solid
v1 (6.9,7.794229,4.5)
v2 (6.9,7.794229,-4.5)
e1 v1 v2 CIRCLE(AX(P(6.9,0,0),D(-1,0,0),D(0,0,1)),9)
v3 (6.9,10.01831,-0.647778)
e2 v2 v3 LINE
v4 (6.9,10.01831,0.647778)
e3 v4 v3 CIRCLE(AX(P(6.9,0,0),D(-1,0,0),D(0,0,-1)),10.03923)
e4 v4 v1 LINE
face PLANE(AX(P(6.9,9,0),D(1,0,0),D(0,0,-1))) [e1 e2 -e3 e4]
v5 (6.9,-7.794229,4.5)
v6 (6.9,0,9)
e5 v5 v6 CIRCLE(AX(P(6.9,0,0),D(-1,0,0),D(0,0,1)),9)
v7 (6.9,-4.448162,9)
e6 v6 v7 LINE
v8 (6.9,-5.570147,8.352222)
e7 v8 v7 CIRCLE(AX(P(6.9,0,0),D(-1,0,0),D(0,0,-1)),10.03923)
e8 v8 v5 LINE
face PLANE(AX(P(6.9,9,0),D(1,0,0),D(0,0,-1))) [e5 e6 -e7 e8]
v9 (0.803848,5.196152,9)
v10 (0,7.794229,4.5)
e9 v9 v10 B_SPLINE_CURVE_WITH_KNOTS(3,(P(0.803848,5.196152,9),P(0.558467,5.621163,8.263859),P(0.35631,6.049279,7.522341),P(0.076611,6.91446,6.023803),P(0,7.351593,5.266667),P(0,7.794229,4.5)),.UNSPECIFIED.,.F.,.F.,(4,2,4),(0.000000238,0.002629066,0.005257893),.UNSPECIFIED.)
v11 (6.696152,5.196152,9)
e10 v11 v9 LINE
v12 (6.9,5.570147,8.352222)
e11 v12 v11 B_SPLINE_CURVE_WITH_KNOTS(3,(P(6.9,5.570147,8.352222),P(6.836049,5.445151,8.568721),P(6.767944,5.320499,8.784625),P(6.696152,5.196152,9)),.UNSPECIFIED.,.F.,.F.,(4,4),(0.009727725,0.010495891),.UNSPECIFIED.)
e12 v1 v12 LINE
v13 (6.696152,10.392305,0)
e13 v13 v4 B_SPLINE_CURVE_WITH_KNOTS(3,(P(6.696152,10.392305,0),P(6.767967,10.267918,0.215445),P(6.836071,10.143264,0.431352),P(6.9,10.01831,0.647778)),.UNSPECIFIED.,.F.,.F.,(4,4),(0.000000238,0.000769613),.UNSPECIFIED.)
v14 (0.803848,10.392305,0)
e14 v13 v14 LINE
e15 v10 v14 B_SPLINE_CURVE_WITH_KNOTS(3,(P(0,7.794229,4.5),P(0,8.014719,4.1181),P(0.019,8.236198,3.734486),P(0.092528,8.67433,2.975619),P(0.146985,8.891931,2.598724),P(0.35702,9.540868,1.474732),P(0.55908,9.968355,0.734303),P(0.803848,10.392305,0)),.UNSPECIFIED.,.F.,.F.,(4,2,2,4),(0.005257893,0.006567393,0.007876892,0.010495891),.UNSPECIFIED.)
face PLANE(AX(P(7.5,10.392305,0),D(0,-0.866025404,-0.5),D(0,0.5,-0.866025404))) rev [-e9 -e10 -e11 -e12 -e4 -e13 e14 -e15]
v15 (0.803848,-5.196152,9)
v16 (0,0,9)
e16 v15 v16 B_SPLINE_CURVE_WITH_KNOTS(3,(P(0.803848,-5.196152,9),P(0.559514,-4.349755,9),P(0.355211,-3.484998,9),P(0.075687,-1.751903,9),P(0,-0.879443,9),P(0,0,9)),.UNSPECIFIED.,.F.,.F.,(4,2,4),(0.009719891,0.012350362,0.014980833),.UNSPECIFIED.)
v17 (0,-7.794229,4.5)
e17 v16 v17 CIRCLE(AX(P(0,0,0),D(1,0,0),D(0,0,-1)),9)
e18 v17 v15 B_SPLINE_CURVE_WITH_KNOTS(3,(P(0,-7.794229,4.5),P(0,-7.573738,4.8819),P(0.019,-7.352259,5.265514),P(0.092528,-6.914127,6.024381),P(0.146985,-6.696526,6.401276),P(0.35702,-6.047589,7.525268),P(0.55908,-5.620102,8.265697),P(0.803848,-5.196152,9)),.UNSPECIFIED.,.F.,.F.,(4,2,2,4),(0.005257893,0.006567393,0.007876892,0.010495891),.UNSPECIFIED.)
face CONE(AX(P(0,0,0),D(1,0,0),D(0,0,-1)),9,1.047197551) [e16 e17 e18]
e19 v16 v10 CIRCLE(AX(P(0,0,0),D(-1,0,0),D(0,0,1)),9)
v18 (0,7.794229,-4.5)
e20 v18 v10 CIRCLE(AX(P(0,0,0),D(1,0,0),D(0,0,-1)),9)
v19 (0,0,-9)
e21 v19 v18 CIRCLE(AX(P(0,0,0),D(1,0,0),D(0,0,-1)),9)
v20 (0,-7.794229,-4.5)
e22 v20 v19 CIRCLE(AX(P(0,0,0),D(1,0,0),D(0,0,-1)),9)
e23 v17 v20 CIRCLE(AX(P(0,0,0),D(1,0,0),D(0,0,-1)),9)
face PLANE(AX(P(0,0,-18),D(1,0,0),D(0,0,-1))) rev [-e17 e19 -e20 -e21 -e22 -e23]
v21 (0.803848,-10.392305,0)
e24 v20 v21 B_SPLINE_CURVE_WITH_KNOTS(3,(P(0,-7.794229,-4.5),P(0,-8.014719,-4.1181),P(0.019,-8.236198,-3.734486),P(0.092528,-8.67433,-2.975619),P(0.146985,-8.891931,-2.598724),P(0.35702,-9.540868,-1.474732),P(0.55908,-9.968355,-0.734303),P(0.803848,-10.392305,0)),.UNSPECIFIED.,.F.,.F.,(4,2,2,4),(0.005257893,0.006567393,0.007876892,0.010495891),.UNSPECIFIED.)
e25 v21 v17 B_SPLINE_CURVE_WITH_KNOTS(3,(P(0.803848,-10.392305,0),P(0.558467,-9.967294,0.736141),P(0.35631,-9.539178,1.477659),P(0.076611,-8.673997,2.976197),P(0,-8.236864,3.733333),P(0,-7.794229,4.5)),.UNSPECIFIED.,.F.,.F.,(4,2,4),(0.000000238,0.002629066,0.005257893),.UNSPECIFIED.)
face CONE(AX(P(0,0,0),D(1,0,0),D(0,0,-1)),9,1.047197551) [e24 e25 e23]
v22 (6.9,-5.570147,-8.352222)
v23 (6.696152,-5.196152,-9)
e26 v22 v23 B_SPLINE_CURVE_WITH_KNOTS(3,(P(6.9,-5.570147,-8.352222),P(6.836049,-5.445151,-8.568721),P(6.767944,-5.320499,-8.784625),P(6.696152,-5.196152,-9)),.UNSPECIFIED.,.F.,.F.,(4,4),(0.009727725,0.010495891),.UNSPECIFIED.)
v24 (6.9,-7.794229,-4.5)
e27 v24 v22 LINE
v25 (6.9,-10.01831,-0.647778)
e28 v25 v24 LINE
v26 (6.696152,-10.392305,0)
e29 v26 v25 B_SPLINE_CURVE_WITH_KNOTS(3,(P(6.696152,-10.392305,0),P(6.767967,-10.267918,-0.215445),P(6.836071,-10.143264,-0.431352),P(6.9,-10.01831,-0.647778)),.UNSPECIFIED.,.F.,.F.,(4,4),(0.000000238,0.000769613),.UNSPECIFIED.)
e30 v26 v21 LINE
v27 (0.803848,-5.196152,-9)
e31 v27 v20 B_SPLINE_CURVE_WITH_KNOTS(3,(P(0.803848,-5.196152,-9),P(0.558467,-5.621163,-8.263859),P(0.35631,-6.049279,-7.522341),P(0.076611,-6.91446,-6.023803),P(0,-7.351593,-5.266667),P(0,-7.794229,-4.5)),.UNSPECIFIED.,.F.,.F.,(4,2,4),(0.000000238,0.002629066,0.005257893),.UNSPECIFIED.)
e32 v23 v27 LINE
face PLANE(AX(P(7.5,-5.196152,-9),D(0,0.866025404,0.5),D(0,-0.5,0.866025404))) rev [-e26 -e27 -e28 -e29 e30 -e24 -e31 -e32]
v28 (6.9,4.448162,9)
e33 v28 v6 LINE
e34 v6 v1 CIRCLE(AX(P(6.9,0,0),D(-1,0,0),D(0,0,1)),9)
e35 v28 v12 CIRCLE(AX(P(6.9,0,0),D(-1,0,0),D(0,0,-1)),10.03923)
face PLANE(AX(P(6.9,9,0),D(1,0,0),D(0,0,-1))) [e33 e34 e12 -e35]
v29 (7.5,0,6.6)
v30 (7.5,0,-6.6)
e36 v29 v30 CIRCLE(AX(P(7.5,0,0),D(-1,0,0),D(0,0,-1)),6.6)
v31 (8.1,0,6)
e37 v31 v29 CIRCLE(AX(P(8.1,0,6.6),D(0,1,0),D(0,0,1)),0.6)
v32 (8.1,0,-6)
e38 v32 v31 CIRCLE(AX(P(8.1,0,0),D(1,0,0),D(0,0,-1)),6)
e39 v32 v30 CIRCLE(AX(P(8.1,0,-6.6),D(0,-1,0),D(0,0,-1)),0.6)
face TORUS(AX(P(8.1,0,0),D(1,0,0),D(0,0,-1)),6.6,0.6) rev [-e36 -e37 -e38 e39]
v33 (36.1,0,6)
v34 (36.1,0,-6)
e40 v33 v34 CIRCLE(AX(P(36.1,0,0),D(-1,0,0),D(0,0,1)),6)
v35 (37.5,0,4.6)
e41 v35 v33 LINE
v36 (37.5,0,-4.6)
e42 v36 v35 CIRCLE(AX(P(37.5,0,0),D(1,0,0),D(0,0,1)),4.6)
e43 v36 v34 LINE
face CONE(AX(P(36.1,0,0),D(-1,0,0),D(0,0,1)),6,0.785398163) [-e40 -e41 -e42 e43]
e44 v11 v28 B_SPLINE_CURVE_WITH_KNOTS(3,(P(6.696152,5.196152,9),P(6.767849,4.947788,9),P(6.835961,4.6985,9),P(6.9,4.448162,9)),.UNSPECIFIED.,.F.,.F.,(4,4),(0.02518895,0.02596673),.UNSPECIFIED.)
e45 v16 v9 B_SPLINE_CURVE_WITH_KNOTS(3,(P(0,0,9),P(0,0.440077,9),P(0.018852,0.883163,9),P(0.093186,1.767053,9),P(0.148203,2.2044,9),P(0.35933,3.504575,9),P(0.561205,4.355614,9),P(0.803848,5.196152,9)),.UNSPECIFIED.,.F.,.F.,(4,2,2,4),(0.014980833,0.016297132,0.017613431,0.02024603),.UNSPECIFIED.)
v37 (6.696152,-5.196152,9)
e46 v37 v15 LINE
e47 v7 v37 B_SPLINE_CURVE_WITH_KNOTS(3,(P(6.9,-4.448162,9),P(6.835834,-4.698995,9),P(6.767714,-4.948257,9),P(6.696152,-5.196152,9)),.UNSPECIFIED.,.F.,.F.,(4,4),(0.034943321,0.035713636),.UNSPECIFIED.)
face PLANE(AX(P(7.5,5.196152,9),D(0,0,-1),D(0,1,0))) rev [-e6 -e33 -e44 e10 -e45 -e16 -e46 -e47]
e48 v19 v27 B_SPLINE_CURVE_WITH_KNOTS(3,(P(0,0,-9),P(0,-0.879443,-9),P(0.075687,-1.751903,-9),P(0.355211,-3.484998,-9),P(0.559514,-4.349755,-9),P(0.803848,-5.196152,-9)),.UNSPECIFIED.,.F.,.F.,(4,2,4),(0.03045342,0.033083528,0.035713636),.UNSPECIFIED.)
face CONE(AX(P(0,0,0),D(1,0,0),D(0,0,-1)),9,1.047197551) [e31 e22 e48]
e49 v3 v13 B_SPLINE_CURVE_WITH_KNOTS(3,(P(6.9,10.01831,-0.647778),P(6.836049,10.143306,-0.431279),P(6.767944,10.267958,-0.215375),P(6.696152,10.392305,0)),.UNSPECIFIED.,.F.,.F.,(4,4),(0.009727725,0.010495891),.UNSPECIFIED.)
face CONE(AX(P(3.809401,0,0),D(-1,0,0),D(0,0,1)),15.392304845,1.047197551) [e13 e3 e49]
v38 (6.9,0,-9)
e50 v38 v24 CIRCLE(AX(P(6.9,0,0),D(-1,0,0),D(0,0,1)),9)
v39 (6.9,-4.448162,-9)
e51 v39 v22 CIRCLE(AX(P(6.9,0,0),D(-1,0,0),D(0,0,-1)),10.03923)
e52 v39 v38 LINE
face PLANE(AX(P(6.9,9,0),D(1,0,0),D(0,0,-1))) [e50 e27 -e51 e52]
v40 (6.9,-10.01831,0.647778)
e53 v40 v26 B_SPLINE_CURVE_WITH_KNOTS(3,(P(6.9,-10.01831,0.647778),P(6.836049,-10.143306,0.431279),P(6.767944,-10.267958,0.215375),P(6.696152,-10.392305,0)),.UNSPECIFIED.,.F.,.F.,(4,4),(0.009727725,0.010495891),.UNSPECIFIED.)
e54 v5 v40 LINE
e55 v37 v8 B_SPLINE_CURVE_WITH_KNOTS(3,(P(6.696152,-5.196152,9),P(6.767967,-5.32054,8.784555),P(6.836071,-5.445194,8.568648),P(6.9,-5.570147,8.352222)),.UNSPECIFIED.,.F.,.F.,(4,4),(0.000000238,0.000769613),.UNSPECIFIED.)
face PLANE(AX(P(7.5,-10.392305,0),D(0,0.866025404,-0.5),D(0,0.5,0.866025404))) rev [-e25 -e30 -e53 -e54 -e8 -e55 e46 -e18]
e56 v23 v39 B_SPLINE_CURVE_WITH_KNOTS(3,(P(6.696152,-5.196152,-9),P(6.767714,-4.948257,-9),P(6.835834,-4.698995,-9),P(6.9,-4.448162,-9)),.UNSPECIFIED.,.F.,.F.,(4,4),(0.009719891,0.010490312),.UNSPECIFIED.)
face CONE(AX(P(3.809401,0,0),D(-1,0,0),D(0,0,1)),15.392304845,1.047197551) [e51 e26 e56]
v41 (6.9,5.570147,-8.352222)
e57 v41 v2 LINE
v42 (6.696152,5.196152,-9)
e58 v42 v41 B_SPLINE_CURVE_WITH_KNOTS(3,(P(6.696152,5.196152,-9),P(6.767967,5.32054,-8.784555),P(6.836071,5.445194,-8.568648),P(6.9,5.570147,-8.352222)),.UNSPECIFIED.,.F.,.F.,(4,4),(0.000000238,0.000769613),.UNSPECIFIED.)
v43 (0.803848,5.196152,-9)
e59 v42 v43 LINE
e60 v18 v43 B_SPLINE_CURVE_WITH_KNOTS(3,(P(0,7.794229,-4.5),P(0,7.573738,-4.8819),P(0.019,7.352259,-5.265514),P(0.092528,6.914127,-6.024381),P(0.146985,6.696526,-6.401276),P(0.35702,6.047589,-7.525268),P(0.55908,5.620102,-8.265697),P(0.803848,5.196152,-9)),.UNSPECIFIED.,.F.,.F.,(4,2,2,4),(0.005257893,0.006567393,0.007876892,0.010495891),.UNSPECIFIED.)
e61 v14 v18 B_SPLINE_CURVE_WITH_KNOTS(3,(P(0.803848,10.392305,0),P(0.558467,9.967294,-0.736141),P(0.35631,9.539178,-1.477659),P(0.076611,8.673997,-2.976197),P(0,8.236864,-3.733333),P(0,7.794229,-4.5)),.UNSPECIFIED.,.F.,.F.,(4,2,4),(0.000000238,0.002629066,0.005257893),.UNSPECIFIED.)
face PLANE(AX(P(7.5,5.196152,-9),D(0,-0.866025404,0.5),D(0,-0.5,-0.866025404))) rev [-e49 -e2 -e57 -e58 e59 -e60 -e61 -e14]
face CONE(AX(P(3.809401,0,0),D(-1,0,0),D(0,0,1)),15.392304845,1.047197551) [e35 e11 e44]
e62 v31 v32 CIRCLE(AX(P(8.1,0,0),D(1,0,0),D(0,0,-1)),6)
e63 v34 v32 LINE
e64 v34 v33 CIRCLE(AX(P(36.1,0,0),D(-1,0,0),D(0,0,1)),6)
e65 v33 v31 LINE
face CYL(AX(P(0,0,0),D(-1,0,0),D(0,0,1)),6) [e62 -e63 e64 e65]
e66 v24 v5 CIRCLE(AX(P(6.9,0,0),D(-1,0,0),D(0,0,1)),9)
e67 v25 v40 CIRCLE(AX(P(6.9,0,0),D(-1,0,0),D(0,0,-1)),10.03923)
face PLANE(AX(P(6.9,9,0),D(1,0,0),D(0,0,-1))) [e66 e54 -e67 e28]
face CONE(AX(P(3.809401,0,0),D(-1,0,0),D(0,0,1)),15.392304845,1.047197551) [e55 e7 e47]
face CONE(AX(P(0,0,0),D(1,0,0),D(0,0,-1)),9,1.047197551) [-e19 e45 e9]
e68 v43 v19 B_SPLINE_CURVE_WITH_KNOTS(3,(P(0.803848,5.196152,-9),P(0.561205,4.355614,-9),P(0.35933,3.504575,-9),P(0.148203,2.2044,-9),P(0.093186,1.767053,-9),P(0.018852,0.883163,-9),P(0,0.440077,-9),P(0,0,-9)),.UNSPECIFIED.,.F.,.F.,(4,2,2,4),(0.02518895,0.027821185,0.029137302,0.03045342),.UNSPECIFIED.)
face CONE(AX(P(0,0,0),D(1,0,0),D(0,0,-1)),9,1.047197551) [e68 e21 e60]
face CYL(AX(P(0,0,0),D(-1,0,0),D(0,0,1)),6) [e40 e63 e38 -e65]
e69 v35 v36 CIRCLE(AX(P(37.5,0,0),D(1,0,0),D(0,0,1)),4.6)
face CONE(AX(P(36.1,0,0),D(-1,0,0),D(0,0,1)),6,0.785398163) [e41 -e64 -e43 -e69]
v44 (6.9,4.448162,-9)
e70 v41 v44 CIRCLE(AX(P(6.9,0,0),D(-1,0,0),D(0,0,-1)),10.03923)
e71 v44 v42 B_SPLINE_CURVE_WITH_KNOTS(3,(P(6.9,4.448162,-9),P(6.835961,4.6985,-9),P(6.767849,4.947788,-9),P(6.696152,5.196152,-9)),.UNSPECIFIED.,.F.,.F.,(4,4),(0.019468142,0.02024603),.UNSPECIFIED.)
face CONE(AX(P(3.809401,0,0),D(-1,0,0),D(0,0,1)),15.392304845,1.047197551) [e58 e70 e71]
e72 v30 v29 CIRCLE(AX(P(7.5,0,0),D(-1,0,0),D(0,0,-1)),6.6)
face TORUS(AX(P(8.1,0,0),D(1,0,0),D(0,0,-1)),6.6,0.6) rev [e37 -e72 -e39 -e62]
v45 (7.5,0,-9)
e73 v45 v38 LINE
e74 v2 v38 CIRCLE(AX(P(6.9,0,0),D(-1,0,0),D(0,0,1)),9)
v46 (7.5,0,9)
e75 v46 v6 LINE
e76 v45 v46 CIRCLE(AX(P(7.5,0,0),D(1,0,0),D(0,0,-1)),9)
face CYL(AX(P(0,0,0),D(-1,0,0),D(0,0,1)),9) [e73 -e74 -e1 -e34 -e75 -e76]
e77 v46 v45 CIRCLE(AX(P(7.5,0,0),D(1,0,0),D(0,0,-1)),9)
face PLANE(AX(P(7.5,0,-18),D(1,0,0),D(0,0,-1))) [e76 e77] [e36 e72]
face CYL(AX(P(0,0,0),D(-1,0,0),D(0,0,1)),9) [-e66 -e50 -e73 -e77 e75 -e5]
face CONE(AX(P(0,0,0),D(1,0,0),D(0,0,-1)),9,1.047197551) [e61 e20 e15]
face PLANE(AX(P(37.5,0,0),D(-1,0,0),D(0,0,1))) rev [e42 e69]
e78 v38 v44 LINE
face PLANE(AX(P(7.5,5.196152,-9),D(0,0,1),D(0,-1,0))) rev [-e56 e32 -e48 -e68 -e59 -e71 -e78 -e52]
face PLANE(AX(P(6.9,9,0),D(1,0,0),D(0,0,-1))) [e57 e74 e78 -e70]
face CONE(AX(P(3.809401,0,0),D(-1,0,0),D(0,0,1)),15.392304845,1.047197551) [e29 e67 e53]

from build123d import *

# Parameters (mm, degrees)
EXTRUDE_360_DEPTH = 7.5
SKETCH_4_W        = 0.6
SKETCH_4_H        = 11.392304845
CHAMFER_1921_SIZE = 1.4
FILLET_1966_R     = 0.6


with BuildPart() as part:
    # 草图1 → Extrude 360 (new body)
    with BuildSketch(Plane(origin=(0, 0, 0), x_dir=(0, 0, -1), z_dir=(1, 0, 0))):
        Polygon((9, 5.196152423), (9, -5.196152423), (0, -10.392304845), (-9, -5.196152423), (-9, 5.196152423), (0, 10.392304845), align=None)
    extrude(amount=EXTRUDE_360_DEPTH)

    # 草图2 → 凸台-旋转1 (revolve)
    with BuildSketch(Plane.XY, mode=Mode.PRIVATE) as revolve_1_sk:
        Polygon((0, 0), (37.5, 0), (37.5, 4.4845), (37.5, 6), (0, 6), align=None)
    revolve(revolve_1_sk.sketch.rotate(Axis((0, 0, 0), (1, 0, 0)), 90), axis=Axis((0, 0, 0), (1, 0, 0)))

    # 草图3 → 切除-旋转1 (revolve, cut)
    with BuildSketch(Plane.XY):
        Polygon((0, 9), (3.690598923, 15.392304845), (3.690598923, 20.392304845), (-10, 20.392304845), (-10, 9), align=None)
    revolve(axis=Axis((0, 0, 0), (1, 0, 0)), mode=Mode.SUBTRACT)

    # 草图5 → 切除-旋转2 (revolve, cut)
    with BuildSketch(Plane.XY):
        Polygon((7.5, 9), (3.809401077, 15.392304845), (3.809401077, 20.392304845), (13.809401077, 20.392304845), (13.809401077, 9), align=None)
    revolve(axis=Axis((0, 0, 0), (1, 0, 0)), mode=Mode.SUBTRACT)

    # 草图4 → 切除-旋转3 (revolve, cut)
    with BuildSketch(Plane.XY, mode=Mode.PRIVATE) as cut_revolve_3_sk:
        with Locations((7.2, 14.696152423)):
            Rectangle(SKETCH_4_W, SKETCH_4_H)
    revolve(cut_revolve_3_sk.sketch.rotate(Axis((0, 0, 0), (1, 0, 0)), 270), axis=Axis((0, 0, 0), (1, 0, 0)), mode=Mode.SUBTRACT)

    # Chamfer 1921
    chamfer_1921_edges = [part.edges().sort_by_distance(p)[0] for p in [
        (37.5, 0, -6),
    ]]
    chamfer(chamfer_1921_edges, length=CHAMFER_1921_SIZE)

    # Fillet 1966
    fillet_1966_edges = [part.edges().sort_by_distance(p)[0] for p in [
        (7.5, 0, -6),
    ]]
    fillet(fillet_1966_edges, radius=FILLET_1966_R)


solid = part.part
